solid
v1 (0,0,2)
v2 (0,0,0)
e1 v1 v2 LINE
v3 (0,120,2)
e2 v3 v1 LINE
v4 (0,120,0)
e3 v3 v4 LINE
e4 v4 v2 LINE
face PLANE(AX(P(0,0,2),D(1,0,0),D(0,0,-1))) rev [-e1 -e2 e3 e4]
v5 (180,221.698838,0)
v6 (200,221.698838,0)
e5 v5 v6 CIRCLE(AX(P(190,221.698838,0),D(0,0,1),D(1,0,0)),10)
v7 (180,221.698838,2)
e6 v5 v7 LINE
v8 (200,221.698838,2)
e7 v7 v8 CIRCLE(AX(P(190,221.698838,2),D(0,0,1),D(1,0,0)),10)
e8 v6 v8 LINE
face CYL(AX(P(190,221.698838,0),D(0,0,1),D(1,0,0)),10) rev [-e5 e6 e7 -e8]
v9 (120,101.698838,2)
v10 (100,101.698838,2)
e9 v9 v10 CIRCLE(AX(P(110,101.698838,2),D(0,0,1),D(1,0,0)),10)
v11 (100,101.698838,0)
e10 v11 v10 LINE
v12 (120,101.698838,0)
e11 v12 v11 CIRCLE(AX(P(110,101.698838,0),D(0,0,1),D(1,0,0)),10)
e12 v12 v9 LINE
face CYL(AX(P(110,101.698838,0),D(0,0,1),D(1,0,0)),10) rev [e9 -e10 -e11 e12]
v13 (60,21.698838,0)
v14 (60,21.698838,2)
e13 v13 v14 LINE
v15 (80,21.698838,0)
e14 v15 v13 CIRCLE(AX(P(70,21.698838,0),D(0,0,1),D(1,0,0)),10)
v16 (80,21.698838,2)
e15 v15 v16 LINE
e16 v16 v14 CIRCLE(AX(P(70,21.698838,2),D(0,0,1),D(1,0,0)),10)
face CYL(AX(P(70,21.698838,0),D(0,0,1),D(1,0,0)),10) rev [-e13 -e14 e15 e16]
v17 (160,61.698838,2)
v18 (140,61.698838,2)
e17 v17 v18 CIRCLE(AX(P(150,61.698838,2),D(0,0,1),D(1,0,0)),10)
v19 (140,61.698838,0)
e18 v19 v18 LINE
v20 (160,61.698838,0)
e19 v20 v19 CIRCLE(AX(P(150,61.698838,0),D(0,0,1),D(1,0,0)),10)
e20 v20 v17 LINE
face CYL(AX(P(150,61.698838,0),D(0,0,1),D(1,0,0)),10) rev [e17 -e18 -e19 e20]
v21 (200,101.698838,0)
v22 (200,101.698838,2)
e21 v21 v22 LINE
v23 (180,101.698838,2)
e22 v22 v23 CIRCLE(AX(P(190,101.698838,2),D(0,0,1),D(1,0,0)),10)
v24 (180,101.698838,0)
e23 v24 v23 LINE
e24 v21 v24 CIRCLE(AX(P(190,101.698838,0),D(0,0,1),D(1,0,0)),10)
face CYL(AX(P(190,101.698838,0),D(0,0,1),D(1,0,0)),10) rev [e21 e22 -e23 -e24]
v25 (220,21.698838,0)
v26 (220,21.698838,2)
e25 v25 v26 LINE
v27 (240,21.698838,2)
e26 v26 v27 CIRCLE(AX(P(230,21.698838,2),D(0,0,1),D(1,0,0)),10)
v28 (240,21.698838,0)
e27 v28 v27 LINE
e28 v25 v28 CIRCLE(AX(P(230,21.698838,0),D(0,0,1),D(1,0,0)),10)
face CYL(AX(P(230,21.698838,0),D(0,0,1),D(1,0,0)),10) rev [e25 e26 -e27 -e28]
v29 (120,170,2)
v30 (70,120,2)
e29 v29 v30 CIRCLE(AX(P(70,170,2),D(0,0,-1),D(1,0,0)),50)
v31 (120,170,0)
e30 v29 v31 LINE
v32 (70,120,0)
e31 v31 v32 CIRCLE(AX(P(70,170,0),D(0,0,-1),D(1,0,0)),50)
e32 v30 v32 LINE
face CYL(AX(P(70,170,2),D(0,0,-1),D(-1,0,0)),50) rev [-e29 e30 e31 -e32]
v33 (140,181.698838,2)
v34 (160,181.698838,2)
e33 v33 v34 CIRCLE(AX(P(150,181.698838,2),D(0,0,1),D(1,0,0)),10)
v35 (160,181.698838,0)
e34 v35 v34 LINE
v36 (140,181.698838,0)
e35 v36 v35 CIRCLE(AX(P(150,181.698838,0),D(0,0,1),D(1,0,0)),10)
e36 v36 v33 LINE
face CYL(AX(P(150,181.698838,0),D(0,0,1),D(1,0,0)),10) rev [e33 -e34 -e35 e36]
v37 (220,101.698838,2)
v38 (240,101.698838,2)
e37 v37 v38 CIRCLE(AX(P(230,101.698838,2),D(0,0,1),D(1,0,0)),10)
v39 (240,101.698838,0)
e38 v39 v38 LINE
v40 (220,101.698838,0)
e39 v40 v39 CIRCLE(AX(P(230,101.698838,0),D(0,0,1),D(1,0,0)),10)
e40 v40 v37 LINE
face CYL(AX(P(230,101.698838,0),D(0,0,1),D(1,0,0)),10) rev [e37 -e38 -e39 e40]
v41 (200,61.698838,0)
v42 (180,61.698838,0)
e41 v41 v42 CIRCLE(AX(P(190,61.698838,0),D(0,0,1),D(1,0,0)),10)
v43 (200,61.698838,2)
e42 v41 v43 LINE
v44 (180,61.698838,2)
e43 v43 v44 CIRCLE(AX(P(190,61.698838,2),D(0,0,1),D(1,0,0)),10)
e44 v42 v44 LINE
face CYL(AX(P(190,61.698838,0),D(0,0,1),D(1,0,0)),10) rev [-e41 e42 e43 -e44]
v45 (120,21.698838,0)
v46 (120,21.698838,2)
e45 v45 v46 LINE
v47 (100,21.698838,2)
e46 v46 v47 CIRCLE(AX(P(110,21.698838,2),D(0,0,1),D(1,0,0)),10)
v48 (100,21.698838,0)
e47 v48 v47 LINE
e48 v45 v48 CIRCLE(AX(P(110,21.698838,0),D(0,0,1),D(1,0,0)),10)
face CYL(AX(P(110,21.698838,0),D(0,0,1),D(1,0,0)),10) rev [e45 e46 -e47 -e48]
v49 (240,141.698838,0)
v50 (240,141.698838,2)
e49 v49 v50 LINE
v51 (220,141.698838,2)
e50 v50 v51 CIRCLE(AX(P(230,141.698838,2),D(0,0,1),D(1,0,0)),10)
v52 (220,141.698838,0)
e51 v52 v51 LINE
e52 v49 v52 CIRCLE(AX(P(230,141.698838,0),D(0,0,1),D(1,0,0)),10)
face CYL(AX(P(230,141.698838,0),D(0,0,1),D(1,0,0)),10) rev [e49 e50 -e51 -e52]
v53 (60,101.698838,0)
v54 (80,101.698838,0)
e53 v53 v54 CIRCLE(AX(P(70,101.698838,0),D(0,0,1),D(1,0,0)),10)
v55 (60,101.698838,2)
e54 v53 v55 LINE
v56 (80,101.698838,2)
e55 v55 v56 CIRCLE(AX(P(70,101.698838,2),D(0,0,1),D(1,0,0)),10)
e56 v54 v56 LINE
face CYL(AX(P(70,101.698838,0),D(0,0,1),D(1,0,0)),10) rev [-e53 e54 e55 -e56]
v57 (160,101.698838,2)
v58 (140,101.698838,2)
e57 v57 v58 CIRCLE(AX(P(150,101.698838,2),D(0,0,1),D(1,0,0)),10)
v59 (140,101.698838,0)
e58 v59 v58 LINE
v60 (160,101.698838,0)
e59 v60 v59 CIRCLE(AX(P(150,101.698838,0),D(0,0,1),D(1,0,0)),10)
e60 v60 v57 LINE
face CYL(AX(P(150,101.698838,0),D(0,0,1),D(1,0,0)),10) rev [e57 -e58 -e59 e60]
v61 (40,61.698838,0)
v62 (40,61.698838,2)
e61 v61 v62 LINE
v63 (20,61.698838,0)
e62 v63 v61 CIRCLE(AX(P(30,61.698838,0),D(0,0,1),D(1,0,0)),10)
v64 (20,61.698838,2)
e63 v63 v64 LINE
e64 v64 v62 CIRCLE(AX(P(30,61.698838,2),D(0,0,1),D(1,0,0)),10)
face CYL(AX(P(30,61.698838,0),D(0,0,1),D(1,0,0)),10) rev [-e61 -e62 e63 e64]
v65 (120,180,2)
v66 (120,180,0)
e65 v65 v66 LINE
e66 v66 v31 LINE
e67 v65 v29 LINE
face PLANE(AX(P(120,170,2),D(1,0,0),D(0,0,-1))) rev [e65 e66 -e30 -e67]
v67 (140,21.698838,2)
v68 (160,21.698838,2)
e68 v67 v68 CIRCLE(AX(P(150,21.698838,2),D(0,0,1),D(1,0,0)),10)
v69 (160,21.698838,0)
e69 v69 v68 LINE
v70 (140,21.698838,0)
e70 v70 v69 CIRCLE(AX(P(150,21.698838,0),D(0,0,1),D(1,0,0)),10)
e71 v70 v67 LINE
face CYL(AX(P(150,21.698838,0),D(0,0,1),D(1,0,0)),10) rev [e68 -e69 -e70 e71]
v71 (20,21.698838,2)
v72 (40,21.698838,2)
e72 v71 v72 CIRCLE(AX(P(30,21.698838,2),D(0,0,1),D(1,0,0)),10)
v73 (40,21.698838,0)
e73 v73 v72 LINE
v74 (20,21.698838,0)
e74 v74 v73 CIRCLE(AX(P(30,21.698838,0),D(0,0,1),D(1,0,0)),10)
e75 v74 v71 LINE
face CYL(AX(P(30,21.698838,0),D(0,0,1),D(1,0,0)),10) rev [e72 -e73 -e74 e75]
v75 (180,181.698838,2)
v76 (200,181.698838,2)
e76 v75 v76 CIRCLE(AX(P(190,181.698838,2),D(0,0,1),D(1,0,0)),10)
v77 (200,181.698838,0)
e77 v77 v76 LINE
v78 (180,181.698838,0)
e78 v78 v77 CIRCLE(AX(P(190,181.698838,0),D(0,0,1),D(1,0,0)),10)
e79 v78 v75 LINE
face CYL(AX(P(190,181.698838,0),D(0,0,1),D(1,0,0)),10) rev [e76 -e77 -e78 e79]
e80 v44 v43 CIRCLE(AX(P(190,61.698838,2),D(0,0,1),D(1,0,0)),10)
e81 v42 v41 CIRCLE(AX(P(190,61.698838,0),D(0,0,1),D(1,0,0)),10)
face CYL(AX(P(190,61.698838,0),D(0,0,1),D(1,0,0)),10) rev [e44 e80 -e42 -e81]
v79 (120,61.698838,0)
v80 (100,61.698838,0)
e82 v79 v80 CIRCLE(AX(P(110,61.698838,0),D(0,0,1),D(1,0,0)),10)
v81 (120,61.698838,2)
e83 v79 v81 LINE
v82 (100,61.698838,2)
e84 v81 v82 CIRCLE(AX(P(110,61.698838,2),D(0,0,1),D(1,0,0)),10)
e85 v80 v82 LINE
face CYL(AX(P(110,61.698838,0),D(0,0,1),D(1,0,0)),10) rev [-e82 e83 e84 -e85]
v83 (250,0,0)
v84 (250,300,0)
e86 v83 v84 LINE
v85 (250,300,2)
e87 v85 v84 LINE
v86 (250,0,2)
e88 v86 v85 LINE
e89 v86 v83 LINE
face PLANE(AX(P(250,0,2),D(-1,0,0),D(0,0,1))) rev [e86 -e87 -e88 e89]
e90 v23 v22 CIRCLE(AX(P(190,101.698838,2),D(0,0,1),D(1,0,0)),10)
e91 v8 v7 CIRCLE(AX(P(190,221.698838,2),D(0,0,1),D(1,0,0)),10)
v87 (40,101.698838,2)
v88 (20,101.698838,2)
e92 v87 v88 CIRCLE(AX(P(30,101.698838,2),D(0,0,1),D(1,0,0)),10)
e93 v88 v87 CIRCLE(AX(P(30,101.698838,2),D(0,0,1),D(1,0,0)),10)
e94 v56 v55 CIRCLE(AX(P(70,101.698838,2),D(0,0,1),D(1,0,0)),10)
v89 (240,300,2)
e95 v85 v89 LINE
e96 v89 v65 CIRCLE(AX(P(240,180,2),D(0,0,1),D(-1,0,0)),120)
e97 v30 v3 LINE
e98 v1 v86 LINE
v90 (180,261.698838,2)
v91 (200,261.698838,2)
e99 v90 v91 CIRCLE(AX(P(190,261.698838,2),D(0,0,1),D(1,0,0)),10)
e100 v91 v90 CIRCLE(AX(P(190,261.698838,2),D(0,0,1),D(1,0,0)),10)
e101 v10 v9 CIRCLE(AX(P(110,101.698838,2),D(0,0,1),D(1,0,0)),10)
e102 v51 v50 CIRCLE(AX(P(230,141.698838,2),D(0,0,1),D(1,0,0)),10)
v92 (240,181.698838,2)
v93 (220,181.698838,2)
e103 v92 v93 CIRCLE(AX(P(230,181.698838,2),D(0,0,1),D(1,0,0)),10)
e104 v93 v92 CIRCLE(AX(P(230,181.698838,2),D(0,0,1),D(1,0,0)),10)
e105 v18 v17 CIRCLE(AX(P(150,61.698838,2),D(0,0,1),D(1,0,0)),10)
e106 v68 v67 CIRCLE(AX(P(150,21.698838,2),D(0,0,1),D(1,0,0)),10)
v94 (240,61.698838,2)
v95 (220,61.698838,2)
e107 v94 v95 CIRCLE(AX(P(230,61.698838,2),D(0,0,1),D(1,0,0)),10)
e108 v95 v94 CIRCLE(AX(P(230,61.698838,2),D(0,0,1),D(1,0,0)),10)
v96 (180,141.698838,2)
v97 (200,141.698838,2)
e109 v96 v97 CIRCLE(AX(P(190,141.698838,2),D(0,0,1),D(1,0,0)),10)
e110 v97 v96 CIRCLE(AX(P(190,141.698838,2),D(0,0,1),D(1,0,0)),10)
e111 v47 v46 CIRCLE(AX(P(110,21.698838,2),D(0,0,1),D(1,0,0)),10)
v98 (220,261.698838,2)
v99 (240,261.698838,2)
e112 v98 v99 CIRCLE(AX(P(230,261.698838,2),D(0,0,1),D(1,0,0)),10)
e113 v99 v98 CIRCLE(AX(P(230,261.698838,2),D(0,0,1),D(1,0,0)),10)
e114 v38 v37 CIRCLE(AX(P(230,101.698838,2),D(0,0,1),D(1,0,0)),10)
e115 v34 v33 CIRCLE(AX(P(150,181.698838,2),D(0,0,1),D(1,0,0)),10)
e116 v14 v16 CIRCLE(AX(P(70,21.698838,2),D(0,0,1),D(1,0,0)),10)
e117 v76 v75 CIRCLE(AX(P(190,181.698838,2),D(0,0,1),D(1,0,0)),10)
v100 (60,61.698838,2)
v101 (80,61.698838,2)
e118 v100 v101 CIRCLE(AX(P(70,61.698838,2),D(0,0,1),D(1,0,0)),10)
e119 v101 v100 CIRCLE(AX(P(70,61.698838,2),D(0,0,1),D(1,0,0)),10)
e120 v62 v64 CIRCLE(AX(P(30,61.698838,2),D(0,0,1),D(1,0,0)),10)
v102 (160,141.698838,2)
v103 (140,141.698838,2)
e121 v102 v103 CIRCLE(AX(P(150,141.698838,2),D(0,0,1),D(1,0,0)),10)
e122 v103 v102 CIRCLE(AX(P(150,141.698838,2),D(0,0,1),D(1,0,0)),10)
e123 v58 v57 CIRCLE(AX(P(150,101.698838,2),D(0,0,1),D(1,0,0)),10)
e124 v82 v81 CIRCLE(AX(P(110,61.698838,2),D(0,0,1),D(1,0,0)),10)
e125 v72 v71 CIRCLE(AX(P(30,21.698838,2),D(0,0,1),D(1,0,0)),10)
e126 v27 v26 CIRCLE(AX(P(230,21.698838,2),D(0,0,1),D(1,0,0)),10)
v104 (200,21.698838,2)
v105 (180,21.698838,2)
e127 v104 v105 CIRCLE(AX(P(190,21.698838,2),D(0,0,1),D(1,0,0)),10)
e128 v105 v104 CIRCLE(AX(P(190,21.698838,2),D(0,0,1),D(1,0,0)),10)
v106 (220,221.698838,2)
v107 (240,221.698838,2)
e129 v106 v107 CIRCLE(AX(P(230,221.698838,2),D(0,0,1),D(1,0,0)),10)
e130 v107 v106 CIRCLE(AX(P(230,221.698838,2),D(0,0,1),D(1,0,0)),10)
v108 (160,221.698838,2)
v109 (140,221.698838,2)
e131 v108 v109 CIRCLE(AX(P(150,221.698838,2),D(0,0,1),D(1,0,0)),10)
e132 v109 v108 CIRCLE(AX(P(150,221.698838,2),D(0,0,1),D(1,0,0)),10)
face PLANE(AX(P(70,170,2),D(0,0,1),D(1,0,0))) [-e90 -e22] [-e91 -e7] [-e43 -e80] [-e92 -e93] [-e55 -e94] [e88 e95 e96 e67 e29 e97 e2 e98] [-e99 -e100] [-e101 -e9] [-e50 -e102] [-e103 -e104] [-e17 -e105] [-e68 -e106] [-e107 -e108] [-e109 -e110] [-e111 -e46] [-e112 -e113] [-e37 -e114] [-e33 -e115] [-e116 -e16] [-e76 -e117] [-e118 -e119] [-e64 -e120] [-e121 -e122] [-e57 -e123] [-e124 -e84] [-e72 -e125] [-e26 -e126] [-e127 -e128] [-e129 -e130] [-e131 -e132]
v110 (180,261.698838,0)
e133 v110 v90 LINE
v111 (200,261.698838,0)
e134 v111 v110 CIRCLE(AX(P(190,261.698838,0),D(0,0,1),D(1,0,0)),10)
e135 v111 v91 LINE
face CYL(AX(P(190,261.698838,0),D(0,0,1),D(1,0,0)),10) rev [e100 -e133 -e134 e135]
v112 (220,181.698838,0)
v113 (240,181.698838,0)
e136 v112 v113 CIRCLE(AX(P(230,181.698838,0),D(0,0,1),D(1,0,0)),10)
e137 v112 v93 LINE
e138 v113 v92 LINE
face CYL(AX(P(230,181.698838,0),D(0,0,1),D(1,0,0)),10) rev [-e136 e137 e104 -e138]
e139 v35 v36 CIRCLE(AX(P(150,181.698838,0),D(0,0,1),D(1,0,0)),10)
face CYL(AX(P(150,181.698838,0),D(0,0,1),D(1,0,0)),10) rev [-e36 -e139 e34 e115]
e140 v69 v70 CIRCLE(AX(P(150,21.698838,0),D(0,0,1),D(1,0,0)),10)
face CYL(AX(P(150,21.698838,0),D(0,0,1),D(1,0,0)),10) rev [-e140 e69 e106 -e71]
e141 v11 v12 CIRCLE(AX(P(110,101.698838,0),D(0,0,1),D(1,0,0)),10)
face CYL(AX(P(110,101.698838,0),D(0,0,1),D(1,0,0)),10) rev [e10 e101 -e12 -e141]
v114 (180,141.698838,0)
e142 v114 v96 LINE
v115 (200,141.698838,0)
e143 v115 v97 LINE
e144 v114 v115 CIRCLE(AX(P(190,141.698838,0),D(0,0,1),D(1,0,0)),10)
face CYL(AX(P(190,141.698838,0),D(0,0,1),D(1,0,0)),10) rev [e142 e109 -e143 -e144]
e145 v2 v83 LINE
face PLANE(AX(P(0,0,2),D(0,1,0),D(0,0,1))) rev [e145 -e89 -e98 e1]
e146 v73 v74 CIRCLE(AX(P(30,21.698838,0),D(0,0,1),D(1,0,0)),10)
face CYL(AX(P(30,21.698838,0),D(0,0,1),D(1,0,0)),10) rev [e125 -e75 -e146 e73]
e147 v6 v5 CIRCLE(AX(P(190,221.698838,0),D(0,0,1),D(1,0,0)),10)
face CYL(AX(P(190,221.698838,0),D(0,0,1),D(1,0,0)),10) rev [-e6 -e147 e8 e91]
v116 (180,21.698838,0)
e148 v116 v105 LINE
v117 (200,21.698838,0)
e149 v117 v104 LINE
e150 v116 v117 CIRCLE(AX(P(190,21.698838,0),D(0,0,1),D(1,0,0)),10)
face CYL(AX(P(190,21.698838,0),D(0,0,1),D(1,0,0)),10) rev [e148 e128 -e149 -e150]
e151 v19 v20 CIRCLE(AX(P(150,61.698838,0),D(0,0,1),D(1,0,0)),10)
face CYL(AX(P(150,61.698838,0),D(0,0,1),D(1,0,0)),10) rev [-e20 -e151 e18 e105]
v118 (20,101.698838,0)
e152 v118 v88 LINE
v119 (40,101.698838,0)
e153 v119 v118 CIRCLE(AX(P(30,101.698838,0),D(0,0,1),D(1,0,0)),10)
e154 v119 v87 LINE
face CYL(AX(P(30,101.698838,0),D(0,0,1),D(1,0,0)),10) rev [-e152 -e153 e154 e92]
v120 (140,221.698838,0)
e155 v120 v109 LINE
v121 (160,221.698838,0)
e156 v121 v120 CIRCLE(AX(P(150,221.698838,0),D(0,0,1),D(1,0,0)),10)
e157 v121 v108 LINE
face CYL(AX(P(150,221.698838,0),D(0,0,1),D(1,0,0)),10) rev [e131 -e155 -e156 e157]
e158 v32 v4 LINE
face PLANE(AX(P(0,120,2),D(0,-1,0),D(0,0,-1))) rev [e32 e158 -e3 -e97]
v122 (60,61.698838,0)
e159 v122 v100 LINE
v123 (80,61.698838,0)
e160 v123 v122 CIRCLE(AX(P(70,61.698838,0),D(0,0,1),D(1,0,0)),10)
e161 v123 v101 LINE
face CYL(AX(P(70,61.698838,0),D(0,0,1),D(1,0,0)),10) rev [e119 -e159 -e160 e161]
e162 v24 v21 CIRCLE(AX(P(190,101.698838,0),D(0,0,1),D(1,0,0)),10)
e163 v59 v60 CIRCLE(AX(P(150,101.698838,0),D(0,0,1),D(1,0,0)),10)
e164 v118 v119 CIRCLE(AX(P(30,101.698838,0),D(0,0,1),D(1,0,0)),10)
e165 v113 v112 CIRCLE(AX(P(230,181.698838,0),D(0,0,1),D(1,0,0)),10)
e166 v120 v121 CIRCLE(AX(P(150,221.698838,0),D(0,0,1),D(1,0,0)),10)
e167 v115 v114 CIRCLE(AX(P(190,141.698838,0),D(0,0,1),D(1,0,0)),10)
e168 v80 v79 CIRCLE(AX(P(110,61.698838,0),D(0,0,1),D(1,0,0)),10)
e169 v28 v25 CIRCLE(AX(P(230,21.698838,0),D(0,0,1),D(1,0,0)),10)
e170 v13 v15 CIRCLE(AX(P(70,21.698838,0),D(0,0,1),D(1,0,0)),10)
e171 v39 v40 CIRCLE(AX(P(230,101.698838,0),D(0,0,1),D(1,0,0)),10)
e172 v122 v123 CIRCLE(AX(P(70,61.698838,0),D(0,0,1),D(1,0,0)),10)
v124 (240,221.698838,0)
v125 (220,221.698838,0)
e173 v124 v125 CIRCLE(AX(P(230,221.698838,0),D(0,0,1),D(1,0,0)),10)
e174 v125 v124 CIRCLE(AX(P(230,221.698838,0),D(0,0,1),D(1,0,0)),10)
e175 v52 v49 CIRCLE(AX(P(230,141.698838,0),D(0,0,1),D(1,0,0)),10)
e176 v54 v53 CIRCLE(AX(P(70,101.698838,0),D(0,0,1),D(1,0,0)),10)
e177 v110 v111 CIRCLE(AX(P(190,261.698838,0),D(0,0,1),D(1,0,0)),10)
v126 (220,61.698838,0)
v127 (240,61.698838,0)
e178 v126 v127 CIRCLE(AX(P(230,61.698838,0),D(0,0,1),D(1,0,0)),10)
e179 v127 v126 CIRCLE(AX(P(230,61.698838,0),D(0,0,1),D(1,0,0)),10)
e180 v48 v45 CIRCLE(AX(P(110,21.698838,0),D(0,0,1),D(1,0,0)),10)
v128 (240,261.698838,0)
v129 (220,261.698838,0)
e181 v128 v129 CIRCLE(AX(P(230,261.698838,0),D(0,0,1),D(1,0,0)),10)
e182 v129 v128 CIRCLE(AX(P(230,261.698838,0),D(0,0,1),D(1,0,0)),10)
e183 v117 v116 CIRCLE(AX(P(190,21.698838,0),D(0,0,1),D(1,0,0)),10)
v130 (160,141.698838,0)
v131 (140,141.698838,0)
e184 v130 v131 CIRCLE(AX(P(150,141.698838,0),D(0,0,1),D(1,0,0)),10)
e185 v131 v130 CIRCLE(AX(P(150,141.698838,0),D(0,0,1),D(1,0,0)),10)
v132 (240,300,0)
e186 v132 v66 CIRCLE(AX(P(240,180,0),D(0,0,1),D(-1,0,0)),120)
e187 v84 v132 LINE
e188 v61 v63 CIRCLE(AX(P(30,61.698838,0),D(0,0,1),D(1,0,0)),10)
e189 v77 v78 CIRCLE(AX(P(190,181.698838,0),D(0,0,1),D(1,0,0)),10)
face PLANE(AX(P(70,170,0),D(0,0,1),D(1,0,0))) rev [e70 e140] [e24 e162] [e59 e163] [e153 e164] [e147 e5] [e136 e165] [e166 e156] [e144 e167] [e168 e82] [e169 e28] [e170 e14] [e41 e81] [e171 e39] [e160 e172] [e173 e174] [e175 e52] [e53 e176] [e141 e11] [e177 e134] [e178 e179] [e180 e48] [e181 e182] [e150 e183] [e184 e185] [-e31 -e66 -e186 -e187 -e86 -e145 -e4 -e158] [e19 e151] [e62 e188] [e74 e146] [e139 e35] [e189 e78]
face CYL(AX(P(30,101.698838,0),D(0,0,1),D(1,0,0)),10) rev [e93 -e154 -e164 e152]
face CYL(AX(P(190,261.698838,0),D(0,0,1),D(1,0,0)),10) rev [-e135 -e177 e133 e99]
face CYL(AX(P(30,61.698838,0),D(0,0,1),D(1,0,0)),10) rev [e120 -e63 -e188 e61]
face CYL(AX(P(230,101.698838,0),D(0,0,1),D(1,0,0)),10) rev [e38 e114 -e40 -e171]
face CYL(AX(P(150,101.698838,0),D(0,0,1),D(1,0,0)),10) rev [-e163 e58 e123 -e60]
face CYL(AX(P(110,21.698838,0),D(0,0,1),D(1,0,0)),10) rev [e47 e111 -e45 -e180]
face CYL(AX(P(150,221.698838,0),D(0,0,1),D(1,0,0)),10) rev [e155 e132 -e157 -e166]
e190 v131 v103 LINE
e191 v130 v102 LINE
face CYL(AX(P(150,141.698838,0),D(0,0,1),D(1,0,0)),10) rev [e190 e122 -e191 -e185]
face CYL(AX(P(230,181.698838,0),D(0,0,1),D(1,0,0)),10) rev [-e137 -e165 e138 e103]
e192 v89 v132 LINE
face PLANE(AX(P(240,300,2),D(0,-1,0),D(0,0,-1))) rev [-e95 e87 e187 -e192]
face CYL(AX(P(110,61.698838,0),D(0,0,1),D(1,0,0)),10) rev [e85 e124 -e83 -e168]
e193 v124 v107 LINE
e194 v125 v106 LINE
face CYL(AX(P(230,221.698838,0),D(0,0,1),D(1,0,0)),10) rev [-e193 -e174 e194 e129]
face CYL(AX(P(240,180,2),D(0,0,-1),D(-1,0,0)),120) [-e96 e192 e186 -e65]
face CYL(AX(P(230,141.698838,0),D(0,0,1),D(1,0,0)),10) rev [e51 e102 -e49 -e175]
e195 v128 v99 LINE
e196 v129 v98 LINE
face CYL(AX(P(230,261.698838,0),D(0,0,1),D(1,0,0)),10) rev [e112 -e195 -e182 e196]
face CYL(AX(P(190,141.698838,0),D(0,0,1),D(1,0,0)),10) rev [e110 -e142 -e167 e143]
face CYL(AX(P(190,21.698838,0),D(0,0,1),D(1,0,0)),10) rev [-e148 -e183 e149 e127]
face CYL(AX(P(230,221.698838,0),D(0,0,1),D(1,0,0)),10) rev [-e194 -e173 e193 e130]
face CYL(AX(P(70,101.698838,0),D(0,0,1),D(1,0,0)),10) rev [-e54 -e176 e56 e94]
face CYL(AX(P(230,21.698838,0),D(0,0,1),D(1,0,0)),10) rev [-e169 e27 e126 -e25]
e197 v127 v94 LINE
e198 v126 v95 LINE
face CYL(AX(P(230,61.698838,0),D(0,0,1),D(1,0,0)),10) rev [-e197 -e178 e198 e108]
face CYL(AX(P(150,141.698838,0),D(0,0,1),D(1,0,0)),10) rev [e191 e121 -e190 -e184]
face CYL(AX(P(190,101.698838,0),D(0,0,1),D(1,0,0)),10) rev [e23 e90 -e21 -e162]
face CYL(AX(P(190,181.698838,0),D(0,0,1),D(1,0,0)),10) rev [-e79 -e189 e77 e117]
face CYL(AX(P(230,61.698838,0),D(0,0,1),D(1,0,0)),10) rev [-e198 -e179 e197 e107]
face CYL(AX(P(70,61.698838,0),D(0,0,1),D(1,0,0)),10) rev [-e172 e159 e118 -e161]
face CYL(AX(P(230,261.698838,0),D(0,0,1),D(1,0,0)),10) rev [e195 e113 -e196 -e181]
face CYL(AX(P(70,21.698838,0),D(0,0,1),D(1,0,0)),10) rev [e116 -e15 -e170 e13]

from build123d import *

# Parameters (mm, degrees)
BOSS_EXTRUDE1_DEPTH = 2
SKETCH2_R           = 10
CUT_EXTRUDE1_DEPTH  = 2


with BuildPart() as part:
    # Sketch1 → Boss-Extrude1 (new body)
    with BuildSketch(Plane.XY):
        with BuildLine():
            Line((0, 0), (250, 0))
            Line((250, 0), (250, 300))
            Line((250, 300), (240, 300))
            ThreePointArc((240, 300), (155.147186258, 264.852813742), (120, 180))
            Line((120, 180), (120, 170))
            ThreePointArc((120, 170), (105.355339059, 134.644660941), (70, 120))
            Line((70, 120), (0, 120))
            Line((0, 120), (0, 0))
        make_face()
    extrude(amount=BOSS_EXTRUDE1_DEPTH)

    # Sketch2 → Cut-Extrude1 (cut)
    with BuildSketch(Plane.XY.offset(2)):
        with Locations((230, 261.698838223)):
            Circle(SKETCH2_R)
        with Locations((190, 261.698838223)):
            Circle(SKETCH2_R)
        with Locations((230, 221.698838223)):
            Circle(SKETCH2_R)
        with Locations((190, 221.698838223)):
            Circle(SKETCH2_R)
        with Locations((230, 181.698838223)):
            Circle(SKETCH2_R)
        with Locations((190, 181.698838223)):
            Circle(SKETCH2_R)
        with Locations((230, 141.698838223)):
            Circle(SKETCH2_R)
        with Locations((190, 141.698838223)):
            Circle(SKETCH2_R)
        with Locations((230, 101.698838223)):
            Circle(SKETCH2_R)
        with Locations((190, 101.698838223)):
            Circle(SKETCH2_R)
        with Locations((230, 61.698838223)):
            Circle(SKETCH2_R)
        with Locations((190, 61.698838223)):
            Circle(SKETCH2_R)
        with Locations((230, 21.698838223)):
            Circle(SKETCH2_R)
        with Locations((190, 21.698838223)):
            Circle(SKETCH2_R)
        with Locations((150, 221.698838223)):
            Circle(SKETCH2_R)
        with Locations((150, 181.698838223)):
            Circle(SKETCH2_R)
        with Locations((150, 141.698838223)):
            Circle(SKETCH2_R)
        with Locations((150, 101.698838223)):
            Circle(SKETCH2_R)
        with Locations((150, 61.698838223)):
            Circle(SKETCH2_R)
        with Locations((150, 21.698838223)):
            Circle(SKETCH2_R)
        with Locations((110, 101.698838223)):
            Circle(SKETCH2_R)
        with Locations((70, 101.698838223)):
            Circle(SKETCH2_R)
        with Locations((30, 101.698838223)):
            Circle(SKETCH2_R)
        with Locations((110, 61.698838223)):
            Circle(SKETCH2_R)
        with Locations((70, 61.698838223)):
            Circle(SKETCH2_R)
        with Locations((30, 61.698838223)):
            Circle(SKETCH2_R)
        with Locations((110, 21.698838223)):
            Circle(SKETCH2_R)
        with Locations((70, 21.698838223)):
            Circle(SKETCH2_R)
        with Locations((30, 21.698838223)):
            Circle(SKETCH2_R)
    extrude(amount=-CUT_EXTRUDE1_DEPTH, mode=Mode.SUBTRACT)


solid = part.part
